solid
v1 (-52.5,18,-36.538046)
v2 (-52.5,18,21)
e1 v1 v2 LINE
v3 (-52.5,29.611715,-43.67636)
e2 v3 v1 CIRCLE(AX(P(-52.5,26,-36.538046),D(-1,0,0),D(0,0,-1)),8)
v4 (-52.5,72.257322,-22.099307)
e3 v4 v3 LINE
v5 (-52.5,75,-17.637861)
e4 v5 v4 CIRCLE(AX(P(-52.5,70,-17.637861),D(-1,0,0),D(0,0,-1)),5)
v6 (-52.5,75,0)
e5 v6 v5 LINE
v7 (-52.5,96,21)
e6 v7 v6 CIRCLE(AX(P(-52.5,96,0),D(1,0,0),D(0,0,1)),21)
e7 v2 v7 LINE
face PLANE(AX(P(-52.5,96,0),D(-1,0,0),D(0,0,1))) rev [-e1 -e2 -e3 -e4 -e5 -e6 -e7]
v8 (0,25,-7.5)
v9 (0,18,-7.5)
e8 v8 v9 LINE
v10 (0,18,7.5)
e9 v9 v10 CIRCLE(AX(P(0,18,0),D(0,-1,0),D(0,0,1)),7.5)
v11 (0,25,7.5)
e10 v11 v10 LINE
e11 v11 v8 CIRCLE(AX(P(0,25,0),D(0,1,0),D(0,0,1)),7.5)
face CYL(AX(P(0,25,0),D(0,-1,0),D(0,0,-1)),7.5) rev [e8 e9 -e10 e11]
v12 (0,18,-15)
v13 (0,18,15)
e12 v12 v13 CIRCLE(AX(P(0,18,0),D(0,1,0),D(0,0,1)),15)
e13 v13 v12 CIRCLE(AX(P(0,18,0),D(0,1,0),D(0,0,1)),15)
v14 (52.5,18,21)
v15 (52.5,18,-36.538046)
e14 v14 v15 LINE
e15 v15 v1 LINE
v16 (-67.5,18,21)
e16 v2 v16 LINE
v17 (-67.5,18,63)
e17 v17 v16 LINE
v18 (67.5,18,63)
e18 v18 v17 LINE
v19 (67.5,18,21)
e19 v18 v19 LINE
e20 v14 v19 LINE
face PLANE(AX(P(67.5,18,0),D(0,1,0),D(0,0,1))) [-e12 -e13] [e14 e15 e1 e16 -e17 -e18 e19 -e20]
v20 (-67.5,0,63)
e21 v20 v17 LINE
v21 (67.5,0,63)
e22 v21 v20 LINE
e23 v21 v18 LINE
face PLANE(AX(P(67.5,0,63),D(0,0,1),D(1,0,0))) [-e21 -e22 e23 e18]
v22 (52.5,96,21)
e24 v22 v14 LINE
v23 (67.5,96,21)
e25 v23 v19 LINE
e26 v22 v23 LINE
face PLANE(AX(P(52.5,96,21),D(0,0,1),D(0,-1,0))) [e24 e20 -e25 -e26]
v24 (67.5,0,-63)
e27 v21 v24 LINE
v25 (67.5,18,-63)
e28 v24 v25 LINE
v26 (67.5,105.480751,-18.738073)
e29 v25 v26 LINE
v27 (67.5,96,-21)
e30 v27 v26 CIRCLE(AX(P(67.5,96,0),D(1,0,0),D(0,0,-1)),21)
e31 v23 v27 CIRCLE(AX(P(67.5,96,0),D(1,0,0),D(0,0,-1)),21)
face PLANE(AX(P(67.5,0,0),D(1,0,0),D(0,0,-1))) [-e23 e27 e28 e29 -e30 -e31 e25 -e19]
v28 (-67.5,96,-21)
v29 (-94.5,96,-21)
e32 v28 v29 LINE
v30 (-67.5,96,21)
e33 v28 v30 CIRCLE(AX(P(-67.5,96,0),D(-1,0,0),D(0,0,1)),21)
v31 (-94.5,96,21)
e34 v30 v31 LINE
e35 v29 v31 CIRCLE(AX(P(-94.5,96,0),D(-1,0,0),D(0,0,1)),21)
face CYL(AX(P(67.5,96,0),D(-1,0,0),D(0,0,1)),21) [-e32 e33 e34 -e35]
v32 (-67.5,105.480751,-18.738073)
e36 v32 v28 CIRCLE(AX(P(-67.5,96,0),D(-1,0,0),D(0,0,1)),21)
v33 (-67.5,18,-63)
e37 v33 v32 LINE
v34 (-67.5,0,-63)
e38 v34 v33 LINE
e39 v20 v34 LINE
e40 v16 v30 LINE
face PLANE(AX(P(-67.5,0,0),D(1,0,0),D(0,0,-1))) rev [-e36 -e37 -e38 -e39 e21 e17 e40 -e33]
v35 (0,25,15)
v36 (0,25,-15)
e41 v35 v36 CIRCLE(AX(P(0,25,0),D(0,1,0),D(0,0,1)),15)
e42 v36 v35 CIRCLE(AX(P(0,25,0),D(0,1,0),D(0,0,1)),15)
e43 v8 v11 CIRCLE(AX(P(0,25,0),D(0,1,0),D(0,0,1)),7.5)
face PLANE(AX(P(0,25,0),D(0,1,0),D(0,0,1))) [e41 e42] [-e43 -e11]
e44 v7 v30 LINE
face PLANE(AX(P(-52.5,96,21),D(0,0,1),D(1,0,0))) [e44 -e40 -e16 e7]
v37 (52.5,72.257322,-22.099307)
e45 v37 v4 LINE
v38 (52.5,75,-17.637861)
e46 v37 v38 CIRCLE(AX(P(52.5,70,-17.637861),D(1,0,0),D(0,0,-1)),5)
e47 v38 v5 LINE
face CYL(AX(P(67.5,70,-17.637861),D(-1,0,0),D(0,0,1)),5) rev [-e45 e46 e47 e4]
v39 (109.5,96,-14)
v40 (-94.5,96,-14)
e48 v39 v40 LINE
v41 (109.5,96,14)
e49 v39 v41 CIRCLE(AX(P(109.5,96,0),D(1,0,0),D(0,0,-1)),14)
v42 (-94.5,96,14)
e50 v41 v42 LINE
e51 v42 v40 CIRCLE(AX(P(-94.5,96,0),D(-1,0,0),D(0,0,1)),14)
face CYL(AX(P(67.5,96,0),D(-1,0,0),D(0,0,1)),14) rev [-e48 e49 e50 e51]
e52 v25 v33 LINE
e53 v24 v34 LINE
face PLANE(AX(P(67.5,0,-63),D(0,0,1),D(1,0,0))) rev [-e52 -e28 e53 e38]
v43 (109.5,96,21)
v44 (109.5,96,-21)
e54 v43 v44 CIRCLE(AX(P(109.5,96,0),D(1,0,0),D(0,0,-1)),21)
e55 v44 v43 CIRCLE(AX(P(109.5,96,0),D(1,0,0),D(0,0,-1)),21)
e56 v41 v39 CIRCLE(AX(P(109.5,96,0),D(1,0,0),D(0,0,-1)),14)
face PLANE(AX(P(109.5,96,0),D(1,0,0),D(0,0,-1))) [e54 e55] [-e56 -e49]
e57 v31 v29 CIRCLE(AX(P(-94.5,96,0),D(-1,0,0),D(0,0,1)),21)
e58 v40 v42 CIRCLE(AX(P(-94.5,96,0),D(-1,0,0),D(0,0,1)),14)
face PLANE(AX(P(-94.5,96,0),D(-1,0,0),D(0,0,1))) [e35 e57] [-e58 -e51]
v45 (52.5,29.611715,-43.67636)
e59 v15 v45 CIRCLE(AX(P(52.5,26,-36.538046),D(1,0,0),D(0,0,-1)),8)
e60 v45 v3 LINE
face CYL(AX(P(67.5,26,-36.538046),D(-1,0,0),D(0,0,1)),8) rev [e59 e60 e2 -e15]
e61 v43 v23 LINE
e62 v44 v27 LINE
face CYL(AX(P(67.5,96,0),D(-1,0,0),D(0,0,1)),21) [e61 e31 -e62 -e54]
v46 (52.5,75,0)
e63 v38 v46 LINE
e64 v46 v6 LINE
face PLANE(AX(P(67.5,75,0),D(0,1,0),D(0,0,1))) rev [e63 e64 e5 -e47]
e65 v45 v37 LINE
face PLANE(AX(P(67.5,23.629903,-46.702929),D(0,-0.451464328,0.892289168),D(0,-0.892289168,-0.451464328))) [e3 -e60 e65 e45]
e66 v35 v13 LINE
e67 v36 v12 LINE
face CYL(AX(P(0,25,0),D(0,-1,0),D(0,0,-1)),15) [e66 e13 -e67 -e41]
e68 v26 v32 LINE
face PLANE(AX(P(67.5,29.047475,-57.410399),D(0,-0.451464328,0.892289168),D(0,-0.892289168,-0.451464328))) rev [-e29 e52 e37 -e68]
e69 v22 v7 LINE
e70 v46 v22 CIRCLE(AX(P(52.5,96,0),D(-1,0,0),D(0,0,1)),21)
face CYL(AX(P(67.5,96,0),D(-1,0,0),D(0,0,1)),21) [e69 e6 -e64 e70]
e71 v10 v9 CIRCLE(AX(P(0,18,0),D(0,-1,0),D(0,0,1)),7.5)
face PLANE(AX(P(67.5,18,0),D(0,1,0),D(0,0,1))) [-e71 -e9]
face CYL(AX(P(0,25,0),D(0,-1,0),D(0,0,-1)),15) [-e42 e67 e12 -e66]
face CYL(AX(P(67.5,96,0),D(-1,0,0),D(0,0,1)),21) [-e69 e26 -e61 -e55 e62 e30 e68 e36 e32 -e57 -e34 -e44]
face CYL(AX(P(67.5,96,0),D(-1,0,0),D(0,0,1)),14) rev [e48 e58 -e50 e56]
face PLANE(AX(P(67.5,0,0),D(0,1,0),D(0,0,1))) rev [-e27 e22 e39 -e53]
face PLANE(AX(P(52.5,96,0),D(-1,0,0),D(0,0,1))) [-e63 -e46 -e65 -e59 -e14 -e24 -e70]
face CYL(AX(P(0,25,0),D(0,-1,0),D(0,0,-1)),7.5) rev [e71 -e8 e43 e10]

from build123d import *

# Parameters (mm, degrees)
PEDESTAL_SECTION_SKETCH_R              = 14
PEDESTAL_BODY_135MM_DEPTH              = 67.5
TUBE_EXTENSION_SHORT_SKETCH_42X_28_R   = 21
TUBE_EXTENSION_SHORT_SKETCH_42X_28_R_2 = 14
TUBE_EXTENSION_27MM_DEPTH              = 27
TUBE_START                             = 42
TUBE_EXTENSION_LONG_SKETCH_42X_28_R    = 21
TUBE_EXTENSION_LONG_SKETCH_42X_28_R_2  = 14
TUBE_EXTENSION_42MM_DEPTH              = 42
SUPPORT_RIB_A_DEPTH                    = 15
SUPPORT_START                          = -15
SUPPORT_RIB_B_DEPTH                    = 15
BASE_BOSS_SKETCH_30X_15_R              = 15
BASE_BOSS_SKETCH_30X_15_R_2            = 7.5
BASE_BOSS_30X_15_DEPTH                 = 7


with BuildPart() as part:
    # Pedestal Section Sketch → Pedestal Body 135mm (new, symmetric)
    with BuildSketch(Plane(origin=(0, 0, 0), x_dir=(0, 0, -1), z_dir=(1, 0, 0))):
        with BuildLine():
            Line((-63, 18), (-63, 0))
            Line((-63, 0), (63, 0))
            Line((63, 0), (63, 18))
            Line((63, 18), (18.738072538, 105.480750896))
            ThreePointArc((18.738072538, 105.480750896), (-17.88988218, 106.997823221), (0, 75))
            Line((0, 75), (17.637861238, 75))
            ThreePointArc((17.637861238, 75), (20.256390577, 74.259495757), (22.099307081, 72.257321642))
            Line((22.099307081, 72.257321642), (43.676359689, 29.611714627))
            ThreePointArc((43.676359689, 29.611714627), (43.353239552, 21.810353059), (36.538046341, 18))
            Line((36.538046341, 18), (-63, 18))
        make_face()
        with Locations((0, 96)):
            Circle(PEDESTAL_SECTION_SKETCH_R, mode=Mode.SUBTRACT)
    extrude(amount=PEDESTAL_BODY_135MM_DEPTH, both=True)

    # Tube Extension Short Sketch Ø42xØ28 → Tube Extension 27mm (add)
    with BuildSketch(Plane.ZY.offset(67.5)):
        with Locations((0, 96)):
            Circle(TUBE_EXTENSION_SHORT_SKETCH_42X_28_R)
        with Locations((0, 96)):
            Circle(TUBE_EXTENSION_SHORT_SKETCH_42X_28_R_2, mode=Mode.SUBTRACT)
    extrude(amount=TUBE_EXTENSION_27MM_DEPTH)

    # Tube Extension Long Sketch Ø42xØ28 → Tube Extension 42mm (add)
    with BuildSketch(Plane(origin=(67.5, 0, 0), x_dir=(0, 0, -1), z_dir=(1, 0, 0)).offset(TUBE_START)):
        with Locations(Location((0, 96, 0), (0, 0, 180))):
            Circle(TUBE_EXTENSION_LONG_SKETCH_42X_28_R)
        with Locations(Location((0, 96, 0), (0, 0, 180))):
            Circle(TUBE_EXTENSION_LONG_SKETCH_42X_28_R_2, mode=Mode.SUBTRACT)
    extrude(amount=-TUBE_EXTENSION_42MM_DEPTH)

    # Support Rib A Sketch → Support Rib A (add)
    with BuildSketch(Plane(origin=(67.5, 0, 0), x_dir=(0, 0, -1), z_dir=(1, 0, 0))):
        with BuildLine():
            Line((-21, 96), (-21, 18))
            Line((-21, 18), (36.538046341, 18))
            ThreePointArc((36.538046341, 18), (43.353239552, 21.810353059), (43.676359689, 29.611714627))
            Line((43.676359689, 29.611714627), (22.099307081, 72.257321642))
            ThreePointArc((22.099307081, 72.257321642), (20.256390577, 74.259495757), (17.637861238, 75))
            Line((17.637861238, 75), (0, 75))
            ThreePointArc((0, 75), (-14.849242405, 81.150757595), (-21, 96))
        make_face()
    extrude(amount=-SUPPORT_RIB_A_DEPTH)

    # Support Rib B Sketch → Support Rib B (add)
    with BuildSketch(Plane.ZY.offset(67.5).offset(SUPPORT_START)):
        with BuildLine():
            Line((21, 96), (21, 18))
            Line((21, 18), (-36.538046341, 18))
            ThreePointArc((-36.538046341, 18), (-43.353239552, 21.810353059), (-43.676359689, 29.611714627))
            Line((-43.676359689, 29.611714627), (-22.099307081, 72.257321642))
            ThreePointArc((-22.099307081, 72.257321642), (-20.256390577, 74.259495757), (-17.637861238, 75))
            Line((-17.637861238, 75), (0, 75))
            ThreePointArc((0, 75), (14.849242405, 81.150757595), (21, 96))
        make_face()
    extrude(amount=SUPPORT_RIB_B_DEPTH)

    # Base Boss Sketch Ø30xØ15 → Base Boss Ø30xØ15 (add)
    with BuildSketch(Plane(origin=(0, 18, 0), x_dir=(1, 0, 0), z_dir=(0, 1, 0))):
        with Locations(Location((0, 0, 0), (0, 0, 270))):
            Circle(BASE_BOSS_SKETCH_30X_15_R)
        with Locations(Location((0, 0, 0), (0, 0, 270))):
            Circle(BASE_BOSS_SKETCH_30X_15_R_2, mode=Mode.SUBTRACT)
    extrude(amount=BASE_BOSS_30X_15_DEPTH)


solid = part.part
